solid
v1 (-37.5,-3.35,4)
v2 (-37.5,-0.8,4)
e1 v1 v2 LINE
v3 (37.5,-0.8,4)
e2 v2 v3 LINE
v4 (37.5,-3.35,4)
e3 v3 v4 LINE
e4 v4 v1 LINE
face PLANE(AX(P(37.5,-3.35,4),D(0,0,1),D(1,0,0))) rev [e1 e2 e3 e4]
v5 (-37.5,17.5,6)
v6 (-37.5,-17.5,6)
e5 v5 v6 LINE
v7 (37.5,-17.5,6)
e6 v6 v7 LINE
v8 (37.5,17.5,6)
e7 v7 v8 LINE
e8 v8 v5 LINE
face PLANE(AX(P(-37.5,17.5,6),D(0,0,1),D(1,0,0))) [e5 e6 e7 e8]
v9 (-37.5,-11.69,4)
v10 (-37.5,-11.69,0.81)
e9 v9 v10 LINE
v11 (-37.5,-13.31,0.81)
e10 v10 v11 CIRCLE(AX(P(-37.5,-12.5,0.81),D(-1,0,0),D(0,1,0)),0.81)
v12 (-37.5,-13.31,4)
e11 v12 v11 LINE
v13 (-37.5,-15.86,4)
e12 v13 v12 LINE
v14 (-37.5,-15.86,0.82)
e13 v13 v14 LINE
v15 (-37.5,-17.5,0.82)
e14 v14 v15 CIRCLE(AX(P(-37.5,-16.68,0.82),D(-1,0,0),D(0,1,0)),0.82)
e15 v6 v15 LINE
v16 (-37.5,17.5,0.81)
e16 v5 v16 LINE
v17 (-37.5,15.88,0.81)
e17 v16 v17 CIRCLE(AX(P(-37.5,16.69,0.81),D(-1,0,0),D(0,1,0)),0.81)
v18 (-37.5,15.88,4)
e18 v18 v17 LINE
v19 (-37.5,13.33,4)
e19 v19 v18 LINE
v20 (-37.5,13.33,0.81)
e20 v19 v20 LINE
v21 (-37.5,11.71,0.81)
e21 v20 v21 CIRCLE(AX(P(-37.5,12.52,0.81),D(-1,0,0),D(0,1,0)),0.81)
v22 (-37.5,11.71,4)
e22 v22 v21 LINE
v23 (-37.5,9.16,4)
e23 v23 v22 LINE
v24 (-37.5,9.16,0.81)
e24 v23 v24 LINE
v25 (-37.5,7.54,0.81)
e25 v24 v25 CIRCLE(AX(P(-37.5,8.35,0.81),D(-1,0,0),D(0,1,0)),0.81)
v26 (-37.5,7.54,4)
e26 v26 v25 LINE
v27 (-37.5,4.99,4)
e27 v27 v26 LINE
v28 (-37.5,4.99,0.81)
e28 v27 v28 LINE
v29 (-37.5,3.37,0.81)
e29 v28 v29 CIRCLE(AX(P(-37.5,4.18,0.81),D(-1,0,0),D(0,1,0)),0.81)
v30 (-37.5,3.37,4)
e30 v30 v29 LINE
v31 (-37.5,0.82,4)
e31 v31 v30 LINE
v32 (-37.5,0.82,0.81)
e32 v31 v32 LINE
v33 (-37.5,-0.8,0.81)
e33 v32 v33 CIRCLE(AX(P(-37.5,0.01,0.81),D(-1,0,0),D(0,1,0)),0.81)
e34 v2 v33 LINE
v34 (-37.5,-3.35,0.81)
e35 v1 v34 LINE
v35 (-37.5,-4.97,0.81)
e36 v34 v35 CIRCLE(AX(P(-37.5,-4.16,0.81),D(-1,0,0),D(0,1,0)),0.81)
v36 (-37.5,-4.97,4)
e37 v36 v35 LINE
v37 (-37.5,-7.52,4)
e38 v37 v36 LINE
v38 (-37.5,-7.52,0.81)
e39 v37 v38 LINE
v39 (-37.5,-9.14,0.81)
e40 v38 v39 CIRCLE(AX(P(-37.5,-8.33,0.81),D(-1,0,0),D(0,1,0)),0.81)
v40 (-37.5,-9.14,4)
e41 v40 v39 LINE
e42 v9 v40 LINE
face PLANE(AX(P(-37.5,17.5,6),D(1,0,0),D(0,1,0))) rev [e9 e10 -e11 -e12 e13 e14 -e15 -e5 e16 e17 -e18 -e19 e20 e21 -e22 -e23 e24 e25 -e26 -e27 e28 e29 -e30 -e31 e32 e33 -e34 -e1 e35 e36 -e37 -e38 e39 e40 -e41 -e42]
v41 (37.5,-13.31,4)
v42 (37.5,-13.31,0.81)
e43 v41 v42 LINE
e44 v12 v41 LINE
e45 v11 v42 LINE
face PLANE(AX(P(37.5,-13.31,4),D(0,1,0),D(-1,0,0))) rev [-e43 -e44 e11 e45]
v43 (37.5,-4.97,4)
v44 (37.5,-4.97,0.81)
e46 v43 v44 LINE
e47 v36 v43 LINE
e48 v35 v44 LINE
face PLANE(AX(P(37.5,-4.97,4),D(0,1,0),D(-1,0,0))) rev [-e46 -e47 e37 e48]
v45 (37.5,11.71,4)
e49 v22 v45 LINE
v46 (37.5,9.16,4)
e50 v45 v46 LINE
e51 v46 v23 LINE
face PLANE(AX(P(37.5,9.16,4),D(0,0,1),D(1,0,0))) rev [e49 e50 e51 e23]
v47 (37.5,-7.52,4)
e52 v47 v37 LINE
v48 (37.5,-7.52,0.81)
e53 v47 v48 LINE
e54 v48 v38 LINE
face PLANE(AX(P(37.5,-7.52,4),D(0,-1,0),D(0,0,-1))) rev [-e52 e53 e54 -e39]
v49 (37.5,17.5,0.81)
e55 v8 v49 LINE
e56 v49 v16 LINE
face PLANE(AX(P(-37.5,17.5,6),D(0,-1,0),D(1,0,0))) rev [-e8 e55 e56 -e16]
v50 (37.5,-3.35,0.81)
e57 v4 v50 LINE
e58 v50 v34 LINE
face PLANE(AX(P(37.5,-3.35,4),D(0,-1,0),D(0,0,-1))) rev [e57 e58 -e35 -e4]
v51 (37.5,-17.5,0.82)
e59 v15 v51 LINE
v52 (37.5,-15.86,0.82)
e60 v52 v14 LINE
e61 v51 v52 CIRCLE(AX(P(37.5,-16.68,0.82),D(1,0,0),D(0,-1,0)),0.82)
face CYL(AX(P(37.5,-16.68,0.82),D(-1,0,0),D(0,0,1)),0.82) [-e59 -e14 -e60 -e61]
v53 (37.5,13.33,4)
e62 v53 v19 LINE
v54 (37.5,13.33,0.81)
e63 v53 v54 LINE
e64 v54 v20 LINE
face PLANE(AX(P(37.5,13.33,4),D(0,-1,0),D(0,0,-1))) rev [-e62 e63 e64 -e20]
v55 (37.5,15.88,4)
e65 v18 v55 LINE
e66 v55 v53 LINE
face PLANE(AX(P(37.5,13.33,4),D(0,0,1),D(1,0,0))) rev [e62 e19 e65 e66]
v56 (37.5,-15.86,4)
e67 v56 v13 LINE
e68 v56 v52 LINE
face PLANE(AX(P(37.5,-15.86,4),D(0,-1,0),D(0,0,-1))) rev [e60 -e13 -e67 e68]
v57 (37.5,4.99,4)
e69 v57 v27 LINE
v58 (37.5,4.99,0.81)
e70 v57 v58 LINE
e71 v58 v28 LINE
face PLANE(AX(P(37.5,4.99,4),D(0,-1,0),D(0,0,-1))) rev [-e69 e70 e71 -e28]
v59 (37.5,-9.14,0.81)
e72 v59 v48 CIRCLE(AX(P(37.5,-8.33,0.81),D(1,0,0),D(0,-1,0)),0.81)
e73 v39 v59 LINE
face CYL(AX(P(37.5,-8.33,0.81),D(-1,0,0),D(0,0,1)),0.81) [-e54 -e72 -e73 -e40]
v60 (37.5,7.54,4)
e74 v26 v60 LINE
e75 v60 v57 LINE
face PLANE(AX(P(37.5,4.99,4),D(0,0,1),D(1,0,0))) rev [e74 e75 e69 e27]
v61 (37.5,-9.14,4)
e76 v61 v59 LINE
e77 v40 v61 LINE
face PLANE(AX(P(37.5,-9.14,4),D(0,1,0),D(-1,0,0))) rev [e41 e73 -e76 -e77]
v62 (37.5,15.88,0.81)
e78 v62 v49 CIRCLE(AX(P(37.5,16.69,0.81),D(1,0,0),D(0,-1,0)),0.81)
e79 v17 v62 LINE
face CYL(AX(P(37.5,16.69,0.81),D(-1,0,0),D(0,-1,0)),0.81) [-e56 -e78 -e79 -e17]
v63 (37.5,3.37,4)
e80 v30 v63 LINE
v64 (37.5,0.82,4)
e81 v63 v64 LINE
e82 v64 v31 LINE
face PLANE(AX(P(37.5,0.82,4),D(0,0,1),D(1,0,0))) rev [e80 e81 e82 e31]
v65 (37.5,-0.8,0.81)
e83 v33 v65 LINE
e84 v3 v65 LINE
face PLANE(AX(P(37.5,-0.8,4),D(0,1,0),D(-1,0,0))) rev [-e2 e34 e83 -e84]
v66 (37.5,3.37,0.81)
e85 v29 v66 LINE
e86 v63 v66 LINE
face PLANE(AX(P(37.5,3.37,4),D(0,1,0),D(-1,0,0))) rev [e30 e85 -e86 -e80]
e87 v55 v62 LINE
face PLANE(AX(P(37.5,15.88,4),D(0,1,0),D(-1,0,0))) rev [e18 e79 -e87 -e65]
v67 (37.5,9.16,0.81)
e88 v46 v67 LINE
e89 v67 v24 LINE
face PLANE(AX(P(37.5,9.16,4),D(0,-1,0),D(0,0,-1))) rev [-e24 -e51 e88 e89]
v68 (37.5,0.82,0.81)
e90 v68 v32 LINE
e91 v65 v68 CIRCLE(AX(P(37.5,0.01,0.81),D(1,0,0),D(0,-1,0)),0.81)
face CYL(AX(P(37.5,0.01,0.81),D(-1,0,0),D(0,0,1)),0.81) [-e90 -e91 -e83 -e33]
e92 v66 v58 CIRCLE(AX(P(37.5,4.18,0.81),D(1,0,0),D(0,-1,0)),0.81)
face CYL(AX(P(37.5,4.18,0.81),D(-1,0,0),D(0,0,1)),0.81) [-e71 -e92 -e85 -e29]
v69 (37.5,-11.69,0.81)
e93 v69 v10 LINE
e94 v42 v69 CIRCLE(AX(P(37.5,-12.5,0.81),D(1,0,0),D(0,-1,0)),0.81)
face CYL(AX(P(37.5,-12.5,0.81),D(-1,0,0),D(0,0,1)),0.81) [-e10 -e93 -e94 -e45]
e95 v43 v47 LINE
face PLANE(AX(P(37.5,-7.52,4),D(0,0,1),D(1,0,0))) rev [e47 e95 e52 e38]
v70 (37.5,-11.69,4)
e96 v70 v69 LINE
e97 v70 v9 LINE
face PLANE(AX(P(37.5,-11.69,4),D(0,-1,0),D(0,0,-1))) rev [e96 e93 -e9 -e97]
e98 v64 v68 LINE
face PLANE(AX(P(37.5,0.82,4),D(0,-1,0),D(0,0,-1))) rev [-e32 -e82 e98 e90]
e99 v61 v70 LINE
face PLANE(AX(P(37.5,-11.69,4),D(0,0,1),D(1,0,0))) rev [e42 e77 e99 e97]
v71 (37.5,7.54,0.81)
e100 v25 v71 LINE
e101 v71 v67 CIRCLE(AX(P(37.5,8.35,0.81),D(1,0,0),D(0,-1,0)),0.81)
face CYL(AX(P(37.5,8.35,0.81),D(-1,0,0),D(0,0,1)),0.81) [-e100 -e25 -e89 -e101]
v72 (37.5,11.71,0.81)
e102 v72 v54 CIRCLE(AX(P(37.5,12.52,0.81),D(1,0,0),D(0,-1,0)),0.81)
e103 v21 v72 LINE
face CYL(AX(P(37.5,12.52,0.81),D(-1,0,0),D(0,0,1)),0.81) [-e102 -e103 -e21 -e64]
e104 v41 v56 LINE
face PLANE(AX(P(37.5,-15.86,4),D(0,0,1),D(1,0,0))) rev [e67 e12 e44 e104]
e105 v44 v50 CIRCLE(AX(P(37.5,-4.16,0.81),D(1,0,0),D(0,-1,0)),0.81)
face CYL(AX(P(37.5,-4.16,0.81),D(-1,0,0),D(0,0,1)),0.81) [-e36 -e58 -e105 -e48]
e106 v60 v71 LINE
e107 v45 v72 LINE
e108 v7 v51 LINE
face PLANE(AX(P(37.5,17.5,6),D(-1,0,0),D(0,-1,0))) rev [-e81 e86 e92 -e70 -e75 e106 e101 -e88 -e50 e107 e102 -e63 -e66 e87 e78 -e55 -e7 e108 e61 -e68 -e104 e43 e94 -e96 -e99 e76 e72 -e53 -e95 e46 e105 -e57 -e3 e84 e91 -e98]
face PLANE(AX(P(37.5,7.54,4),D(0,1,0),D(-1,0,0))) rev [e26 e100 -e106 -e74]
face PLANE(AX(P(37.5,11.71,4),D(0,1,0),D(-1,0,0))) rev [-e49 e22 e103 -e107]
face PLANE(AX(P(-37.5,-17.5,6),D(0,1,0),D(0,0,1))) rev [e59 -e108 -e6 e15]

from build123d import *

# Parameters (mm, degrees)
SKETCH_1_W             = 75
SKETCH_1_H             = 35
EXTRUDE_1_DEPTH        = 6
SKETCH_2_W             = 75
SKETCH_2_H             = 2.55
CUT_EXTRUDE_1_DEPTH    = 4
PATTERN_LINEAR_1_COUNT = 8
PATTERN_LINEAR_1_PITCH = 4.17
FILLET_2_RADIUS        = 0.81
FILLET_2_LENGTH        = 75
FILLET_3_RADIUS        = 0.81
FILLET_3_LENGTH        = 75
FILLET_4_RADIUS        = 0.81
FILLET_4_LENGTH        = 75
FILLET_5_RADIUS        = 0.81
FILLET_5_LENGTH        = 75
FILLET_6_RADIUS        = 0.81
FILLET_6_LENGTH        = 75
FILLET_7_RADIUS        = 0.81
FILLET_7_LENGTH        = 75
FILLET_8_RADIUS        = 0.81
FILLET_8_LENGTH        = 75
FILLET_9_RADIUS        = 0.81
FILLET_9_LENGTH        = 75
FILLET_10_RADIUS       = 0.82
FILLET_10_LENGTH       = 75


with BuildPart() as part:
    # 草图1 → 拉伸1 (new body)
    with BuildSketch(Plane.XY):
        Rectangle(SKETCH_1_W, SKETCH_1_H)
    extrude(amount=EXTRUDE_1_DEPTH)

    # 草图2 → 切除-拉伸1 (cut)
    with BuildSketch(Plane(origin=(0, 0, 0), x_dir=(-1, 0, 0), z_dir=(0, 0, -1))):
        with Locations((0, 14.605)):
            Rectangle(SKETCH_2_W, SKETCH_2_H)
    cut_extrude_1 = extrude(amount=-CUT_EXTRUDE_1_DEPTH, mode=Mode.SUBTRACT)

    # 阵列(线性)1: 切除-拉伸1 ×8
    with Locations(*[(0, -i * PATTERN_LINEAR_1_PITCH, 0) for i in range(1, PATTERN_LINEAR_1_COUNT)]):
        add(cut_extrude_1, mode=Mode.SUBTRACT)

    # 圆角2: full round fillet: the end face becomes a half cylinder, R = half its width
    fillet_2_face = Plane((0, 16.69, 0), x_dir=(-1, 0, 0), z_dir=(0, 0, -1))  # on the end face: x along it, z out of the body
    fillet_2_slab = fillet_2_face.offset(-FILLET_2_RADIUS / 2) * Box(FILLET_2_LENGTH, 2 * FILLET_2_RADIUS, FILLET_2_RADIUS, mode=Mode.PRIVATE)  # the body's end, R deep
    fillet_2_round = Plane((0, 16.69, 0.81), x_dir=(0, 0, -1), z_dir=(-1, 0, 0)) * Cylinder(FILLET_2_RADIUS, FILLET_2_LENGTH, mode=Mode.PRIVATE)  # its axis R under the face
    add(fillet_2_slab - fillet_2_round, mode=Mode.SUBTRACT)

    # 圆角3: full round fillet: the end face becomes a half cylinder, R = half its width
    fillet_3_face = Plane((0, 12.52, 0), x_dir=(1, 0, 0), z_dir=(0, 0, -1))  # on the end face: x along it, z out of the body
    fillet_3_slab = fillet_3_face.offset(-FILLET_3_RADIUS / 2) * Box(FILLET_3_LENGTH, 2 * FILLET_3_RADIUS, FILLET_3_RADIUS, mode=Mode.PRIVATE)  # the body's end, R deep
    fillet_3_round = Plane((0, 12.52, 0.81), x_dir=(0, 0, -1), z_dir=(1, 0, 0)) * Cylinder(FILLET_3_RADIUS, FILLET_3_LENGTH, mode=Mode.PRIVATE)  # its axis R under the face
    add(fillet_3_slab - fillet_3_round, mode=Mode.SUBTRACT)

    # 圆角4: full round fillet: the end face becomes a half cylinder, R = half its width
    fillet_4_face = Plane((0, 8.35, 0), x_dir=(1, 0, 0), z_dir=(0, 0, -1))  # on the end face: x along it, z out of the body
    fillet_4_slab = fillet_4_face.offset(-FILLET_4_RADIUS / 2) * Box(FILLET_4_LENGTH, 2 * FILLET_4_RADIUS, FILLET_4_RADIUS, mode=Mode.PRIVATE)  # the body's end, R deep
    fillet_4_round = Plane((0, 8.35, 0.81), x_dir=(0, 0, -1), z_dir=(1, 0, 0)) * Cylinder(FILLET_4_RADIUS, FILLET_4_LENGTH, mode=Mode.PRIVATE)  # its axis R under the face
    add(fillet_4_slab - fillet_4_round, mode=Mode.SUBTRACT)

    # 圆角5: full round fillet: the end face becomes a half cylinder, R = half its width
    fillet_5_face = Plane((0, 4.18, 0), x_dir=(1, 0, 0), z_dir=(0, 0, -1))  # on the end face: x along it, z out of the body
    fillet_5_slab = fillet_5_face.offset(-FILLET_5_RADIUS / 2) * Box(FILLET_5_LENGTH, 2 * FILLET_5_RADIUS, FILLET_5_RADIUS, mode=Mode.PRIVATE)  # the body's end, R deep
    fillet_5_round = Plane((0, 4.18, 0.81), x_dir=(0, 0, -1), z_dir=(1, 0, 0)) * Cylinder(FILLET_5_RADIUS, FILLET_5_LENGTH, mode=Mode.PRIVATE)  # its axis R under the face
    add(fillet_5_slab - fillet_5_round, mode=Mode.SUBTRACT)

    # 圆角6: full round fillet: the end face becomes a half cylinder, R = half its width
    fillet_6_face = Plane((0, 0.01, 0), x_dir=(1, 0, 0), z_dir=(0, 0, -1))  # on the end face: x along it, z out of the body
    fillet_6_slab = fillet_6_face.offset(-FILLET_6_RADIUS / 2) * Box(FILLET_6_LENGTH, 2 * FILLET_6_RADIUS, FILLET_6_RADIUS, mode=Mode.PRIVATE)  # the body's end, R deep
    fillet_6_round = Plane((0, 0.01, 0.81), x_dir=(0, 0, -1), z_dir=(1, 0, 0)) * Cylinder(FILLET_6_RADIUS, FILLET_6_LENGTH, mode=Mode.PRIVATE)  # its axis R under the face
    add(fillet_6_slab - fillet_6_round, mode=Mode.SUBTRACT)

    # 圆角7: full round fillet: the end face becomes a half cylinder, R = half its width
    fillet_7_face = Plane((0, -4.16, 0), x_dir=(1, 0, 0), z_dir=(0, 0, -1))  # on the end face: x along it, z out of the body
    fillet_7_slab = fillet_7_face.offset(-FILLET_7_RADIUS / 2) * Box(FILLET_7_LENGTH, 2 * FILLET_7_RADIUS, FILLET_7_RADIUS, mode=Mode.PRIVATE)  # the body's end, R deep
    fillet_7_round = Plane((0, -4.16, 0.81), x_dir=(0, 0, -1), z_dir=(1, 0, 0)) * Cylinder(FILLET_7_RADIUS, FILLET_7_LENGTH, mode=Mode.PRIVATE)  # its axis R under the face
    add(fillet_7_slab - fillet_7_round, mode=Mode.SUBTRACT)

    # 圆角8: full round fillet: the end face becomes a half cylinder, R = half its width
    fillet_8_face = Plane((0, -8.33, 0), x_dir=(-1, 0, 0), z_dir=(0, 0, -1))  # on the end face: x along it, z out of the body
    fillet_8_slab = fillet_8_face.offset(-FILLET_8_RADIUS / 2) * Box(FILLET_8_LENGTH, 2 * FILLET_8_RADIUS, FILLET_8_RADIUS, mode=Mode.PRIVATE)  # the body's end, R deep
    fillet_8_round = Plane((0, -8.33, 0.81), x_dir=(0, 0, -1), z_dir=(-1, 0, 0)) * Cylinder(FILLET_8_RADIUS, FILLET_8_LENGTH, mode=Mode.PRIVATE)  # its axis R under the face
    add(fillet_8_slab - fillet_8_round, mode=Mode.SUBTRACT)

    # 圆角9: full round fillet: the end face becomes a half cylinder, R = half its width
    fillet_9_face = Plane((0, -12.5, 0), x_dir=(1, 0, 0), z_dir=(0, 0, -1))  # on the end face: x along it, z out of the body
    fillet_9_slab = fillet_9_face.offset(-FILLET_9_RADIUS / 2) * Box(FILLET_9_LENGTH, 2 * FILLET_9_RADIUS, FILLET_9_RADIUS, mode=Mode.PRIVATE)  # the body's end, R deep
    fillet_9_round = Plane((0, -12.5, 0.81), x_dir=(0, 0, -1), z_dir=(1, 0, 0)) * Cylinder(FILLET_9_RADIUS, FILLET_9_LENGTH, mode=Mode.PRIVATE)  # its axis R under the face
    add(fillet_9_slab - fillet_9_round, mode=Mode.SUBTRACT)

    # 圆角10: full round fillet: the end face becomes a half cylinder, R = half its width
    fillet_10_face = Plane((0, -16.68, 0), x_dir=(1, 0, 0), z_dir=(0, 0, -1))  # on the end face: x along it, z out of the body
    fillet_10_slab = fillet_10_face.offset(-FILLET_10_RADIUS / 2) * Box(FILLET_10_LENGTH, 2 * FILLET_10_RADIUS, FILLET_10_RADIUS, mode=Mode.PRIVATE)  # the body's end, R deep
    fillet_10_round = Plane((0, -16.68, 0.82), x_dir=(0, 0, -1), z_dir=(1, 0, 0)) * Cylinder(FILLET_10_RADIUS, FILLET_10_LENGTH, mode=Mode.PRIVATE)  # its axis R under the face
    add(fillet_10_slab - fillet_10_round, mode=Mode.SUBTRACT)


solid = part.part
